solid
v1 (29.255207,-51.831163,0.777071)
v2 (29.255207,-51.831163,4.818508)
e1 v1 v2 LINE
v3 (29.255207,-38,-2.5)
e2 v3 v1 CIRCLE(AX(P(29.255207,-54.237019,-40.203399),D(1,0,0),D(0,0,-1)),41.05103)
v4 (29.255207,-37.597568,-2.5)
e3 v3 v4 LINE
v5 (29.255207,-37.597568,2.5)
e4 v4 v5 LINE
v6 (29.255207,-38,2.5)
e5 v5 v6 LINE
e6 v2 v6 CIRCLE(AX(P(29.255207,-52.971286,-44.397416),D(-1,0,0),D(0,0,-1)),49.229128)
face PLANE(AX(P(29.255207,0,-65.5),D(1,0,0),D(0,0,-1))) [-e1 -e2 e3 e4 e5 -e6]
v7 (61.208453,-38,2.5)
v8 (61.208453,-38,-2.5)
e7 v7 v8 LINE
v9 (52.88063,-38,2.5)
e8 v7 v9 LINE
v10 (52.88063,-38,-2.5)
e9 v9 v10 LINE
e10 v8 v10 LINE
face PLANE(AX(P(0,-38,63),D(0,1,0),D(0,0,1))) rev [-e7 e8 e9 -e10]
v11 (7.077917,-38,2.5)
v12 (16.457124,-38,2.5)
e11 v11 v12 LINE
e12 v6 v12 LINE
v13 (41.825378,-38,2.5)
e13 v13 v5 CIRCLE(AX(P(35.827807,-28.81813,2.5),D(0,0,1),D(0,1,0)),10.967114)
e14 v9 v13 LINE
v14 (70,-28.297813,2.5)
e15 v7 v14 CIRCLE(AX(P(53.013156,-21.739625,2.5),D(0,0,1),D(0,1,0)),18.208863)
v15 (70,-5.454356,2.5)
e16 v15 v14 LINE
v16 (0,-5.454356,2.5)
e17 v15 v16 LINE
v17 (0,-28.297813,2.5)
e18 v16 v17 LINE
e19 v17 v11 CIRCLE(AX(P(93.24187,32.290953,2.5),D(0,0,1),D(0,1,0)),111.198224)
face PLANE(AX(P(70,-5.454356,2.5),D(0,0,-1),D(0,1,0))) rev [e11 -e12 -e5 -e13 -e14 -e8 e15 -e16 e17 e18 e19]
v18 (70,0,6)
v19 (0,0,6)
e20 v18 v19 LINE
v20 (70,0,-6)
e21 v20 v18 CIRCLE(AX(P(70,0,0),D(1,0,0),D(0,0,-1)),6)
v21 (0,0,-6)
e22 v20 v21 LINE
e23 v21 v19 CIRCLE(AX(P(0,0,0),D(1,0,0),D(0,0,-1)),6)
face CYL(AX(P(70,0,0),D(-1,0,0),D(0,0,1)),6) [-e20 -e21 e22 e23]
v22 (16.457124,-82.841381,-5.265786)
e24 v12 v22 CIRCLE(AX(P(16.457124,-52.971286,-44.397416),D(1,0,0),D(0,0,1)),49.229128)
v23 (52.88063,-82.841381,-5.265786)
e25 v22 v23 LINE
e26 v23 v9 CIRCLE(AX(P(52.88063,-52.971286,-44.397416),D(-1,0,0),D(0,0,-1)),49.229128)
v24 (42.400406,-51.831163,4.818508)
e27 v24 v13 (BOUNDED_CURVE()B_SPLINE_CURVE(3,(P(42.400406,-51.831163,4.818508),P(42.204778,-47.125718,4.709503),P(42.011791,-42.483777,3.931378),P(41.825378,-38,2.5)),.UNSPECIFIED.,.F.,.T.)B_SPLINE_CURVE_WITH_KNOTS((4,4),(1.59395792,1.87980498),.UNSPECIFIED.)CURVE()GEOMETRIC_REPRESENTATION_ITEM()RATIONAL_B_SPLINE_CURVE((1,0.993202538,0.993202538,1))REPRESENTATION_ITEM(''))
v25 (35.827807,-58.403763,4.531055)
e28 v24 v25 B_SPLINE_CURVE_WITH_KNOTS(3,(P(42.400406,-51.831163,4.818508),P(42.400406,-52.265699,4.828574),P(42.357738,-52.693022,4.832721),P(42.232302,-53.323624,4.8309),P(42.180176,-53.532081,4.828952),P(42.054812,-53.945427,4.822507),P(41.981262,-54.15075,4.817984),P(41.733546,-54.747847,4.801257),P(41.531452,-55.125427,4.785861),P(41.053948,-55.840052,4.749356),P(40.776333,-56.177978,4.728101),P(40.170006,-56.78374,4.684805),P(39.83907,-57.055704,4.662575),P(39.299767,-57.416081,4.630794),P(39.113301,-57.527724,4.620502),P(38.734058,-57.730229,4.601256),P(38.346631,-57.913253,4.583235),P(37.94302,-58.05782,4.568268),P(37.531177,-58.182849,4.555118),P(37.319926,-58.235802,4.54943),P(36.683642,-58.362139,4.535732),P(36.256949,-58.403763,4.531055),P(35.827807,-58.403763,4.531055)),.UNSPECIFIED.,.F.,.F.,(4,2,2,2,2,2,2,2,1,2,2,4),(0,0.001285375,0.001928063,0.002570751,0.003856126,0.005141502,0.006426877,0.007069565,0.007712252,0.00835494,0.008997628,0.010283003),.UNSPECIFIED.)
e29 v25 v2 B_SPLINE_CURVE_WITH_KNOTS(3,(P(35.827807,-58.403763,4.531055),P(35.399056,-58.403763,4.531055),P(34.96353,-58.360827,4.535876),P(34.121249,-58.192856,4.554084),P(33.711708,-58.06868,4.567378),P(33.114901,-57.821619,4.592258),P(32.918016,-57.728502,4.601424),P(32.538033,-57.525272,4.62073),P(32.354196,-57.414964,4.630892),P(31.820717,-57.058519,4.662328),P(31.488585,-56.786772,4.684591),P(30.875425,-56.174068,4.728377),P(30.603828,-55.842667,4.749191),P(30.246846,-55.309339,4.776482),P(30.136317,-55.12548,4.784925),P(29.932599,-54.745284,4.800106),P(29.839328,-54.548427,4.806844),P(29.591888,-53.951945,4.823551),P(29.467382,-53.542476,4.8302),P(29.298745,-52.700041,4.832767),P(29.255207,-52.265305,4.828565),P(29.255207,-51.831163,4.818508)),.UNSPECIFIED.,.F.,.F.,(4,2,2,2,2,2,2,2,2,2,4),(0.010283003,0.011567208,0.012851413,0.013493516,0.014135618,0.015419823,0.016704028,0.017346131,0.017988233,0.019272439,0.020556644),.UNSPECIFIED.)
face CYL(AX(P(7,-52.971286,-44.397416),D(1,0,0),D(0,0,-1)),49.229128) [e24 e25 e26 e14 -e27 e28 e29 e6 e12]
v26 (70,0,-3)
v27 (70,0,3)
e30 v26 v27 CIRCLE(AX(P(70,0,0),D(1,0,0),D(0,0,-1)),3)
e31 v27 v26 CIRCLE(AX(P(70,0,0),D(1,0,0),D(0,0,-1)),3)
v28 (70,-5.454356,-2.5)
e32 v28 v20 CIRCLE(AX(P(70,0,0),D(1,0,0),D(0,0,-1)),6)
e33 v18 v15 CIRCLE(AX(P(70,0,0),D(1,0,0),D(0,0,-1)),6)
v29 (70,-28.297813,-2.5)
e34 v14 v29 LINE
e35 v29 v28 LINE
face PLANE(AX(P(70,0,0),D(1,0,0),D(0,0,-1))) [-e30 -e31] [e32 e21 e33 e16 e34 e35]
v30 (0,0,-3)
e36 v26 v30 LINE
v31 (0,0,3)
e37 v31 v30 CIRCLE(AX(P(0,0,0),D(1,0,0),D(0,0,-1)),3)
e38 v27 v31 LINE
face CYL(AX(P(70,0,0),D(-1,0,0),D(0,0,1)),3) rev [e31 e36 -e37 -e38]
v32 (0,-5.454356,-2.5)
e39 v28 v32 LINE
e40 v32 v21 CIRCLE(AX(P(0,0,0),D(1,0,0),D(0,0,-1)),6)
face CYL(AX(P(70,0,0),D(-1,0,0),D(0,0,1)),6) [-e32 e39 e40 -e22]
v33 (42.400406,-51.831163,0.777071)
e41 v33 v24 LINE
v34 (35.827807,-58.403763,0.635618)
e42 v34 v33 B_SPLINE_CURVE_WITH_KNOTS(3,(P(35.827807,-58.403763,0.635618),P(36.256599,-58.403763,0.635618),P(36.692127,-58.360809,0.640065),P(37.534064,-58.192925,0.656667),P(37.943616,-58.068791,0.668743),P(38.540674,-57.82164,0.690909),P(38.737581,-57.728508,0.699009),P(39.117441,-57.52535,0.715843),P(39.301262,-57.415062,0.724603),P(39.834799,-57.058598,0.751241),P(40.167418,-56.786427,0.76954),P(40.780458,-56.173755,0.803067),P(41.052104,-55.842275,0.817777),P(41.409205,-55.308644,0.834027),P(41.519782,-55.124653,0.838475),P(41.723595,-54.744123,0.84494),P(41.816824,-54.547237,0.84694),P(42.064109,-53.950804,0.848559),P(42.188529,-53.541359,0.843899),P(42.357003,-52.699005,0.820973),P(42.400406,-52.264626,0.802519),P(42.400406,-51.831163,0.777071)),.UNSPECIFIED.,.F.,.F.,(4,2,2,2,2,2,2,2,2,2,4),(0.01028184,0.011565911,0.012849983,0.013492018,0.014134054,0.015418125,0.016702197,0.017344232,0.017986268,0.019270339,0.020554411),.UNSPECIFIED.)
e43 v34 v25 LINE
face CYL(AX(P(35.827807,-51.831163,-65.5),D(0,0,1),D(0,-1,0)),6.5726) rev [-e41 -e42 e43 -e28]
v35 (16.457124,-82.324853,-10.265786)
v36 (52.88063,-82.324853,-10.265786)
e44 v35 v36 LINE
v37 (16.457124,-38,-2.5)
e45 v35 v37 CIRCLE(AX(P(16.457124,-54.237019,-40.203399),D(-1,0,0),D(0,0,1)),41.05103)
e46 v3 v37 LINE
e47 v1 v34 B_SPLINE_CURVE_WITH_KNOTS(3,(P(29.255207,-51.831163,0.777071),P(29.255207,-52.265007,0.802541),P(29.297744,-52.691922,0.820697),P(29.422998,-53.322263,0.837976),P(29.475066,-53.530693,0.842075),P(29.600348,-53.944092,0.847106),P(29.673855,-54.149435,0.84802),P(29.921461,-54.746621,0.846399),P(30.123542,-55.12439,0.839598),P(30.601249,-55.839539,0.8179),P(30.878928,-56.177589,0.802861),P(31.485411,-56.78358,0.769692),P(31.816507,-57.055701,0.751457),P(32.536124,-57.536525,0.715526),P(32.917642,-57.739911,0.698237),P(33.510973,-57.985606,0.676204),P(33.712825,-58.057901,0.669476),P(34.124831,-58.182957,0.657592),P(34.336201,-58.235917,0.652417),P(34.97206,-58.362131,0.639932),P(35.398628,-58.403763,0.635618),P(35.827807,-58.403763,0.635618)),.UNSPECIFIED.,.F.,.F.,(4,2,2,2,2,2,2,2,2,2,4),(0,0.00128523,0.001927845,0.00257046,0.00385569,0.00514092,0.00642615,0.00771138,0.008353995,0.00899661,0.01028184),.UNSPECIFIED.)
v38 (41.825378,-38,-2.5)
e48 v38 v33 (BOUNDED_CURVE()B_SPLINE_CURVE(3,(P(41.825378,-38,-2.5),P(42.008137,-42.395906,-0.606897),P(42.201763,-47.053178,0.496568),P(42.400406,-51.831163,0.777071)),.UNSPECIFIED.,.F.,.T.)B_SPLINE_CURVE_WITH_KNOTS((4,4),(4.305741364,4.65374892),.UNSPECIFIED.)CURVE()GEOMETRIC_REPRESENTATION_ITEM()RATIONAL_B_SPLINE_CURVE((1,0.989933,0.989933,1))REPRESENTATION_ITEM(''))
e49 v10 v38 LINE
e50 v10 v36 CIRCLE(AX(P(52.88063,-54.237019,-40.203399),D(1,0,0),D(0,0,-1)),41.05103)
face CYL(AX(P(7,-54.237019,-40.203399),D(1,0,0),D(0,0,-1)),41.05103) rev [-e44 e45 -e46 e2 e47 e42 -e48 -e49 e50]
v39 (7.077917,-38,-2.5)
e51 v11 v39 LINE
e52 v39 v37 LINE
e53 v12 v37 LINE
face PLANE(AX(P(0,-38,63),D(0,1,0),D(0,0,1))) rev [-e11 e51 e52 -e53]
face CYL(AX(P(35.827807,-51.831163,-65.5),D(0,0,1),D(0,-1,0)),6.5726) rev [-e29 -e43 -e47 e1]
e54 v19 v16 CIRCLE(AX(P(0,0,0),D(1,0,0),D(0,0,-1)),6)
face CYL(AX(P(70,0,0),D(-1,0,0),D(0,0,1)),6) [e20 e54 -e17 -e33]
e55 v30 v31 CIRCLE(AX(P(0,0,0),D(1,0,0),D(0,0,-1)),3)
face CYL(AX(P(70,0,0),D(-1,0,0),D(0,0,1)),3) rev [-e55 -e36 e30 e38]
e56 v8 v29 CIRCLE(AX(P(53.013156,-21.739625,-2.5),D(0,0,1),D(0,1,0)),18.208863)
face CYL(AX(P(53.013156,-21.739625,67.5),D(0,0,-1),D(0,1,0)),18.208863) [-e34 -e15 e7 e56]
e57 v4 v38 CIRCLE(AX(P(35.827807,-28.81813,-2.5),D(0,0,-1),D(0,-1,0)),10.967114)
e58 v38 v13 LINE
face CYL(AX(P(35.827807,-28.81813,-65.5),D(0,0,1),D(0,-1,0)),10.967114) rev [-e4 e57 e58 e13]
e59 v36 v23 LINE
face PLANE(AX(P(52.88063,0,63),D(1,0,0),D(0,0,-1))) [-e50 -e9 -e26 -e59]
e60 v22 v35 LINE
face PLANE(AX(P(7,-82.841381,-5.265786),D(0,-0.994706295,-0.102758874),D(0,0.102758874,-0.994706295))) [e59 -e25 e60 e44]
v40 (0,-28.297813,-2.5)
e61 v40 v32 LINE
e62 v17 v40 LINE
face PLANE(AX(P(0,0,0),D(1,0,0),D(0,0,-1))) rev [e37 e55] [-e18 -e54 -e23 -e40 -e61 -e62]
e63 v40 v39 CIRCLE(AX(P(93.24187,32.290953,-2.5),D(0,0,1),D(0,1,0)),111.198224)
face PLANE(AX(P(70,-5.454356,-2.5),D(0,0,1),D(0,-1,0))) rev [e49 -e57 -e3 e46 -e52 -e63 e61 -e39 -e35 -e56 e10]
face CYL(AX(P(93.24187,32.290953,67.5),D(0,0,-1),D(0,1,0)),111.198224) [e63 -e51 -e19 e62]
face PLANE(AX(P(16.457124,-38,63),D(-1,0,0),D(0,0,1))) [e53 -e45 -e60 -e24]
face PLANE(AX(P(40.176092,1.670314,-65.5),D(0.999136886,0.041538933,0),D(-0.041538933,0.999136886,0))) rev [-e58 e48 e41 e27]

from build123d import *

# Parameters (mm, degrees)
BARREL_AND_PLATE_PROFILE_SKETCH_R = 3
BARREL_AND_PLATE_70MM_DEPTH       = 70
PLATE_PROFILE_TRIM_DEPTH          = 70
LOWER_PLATE_DEPTH                 = 63
KEYHOLE_CUT_DEPTH                 = 63
KEYHOLE_CUT_DEPTH_BACK            = 63
KEYHOLE_SKETCH_W                  = 3.828036988
KEYHOLE_SKETCH_H                  = 46.115634491
KEYHOLE_SKETCH_W_2                = 17.383946001
CORNER_CHAMFER_CUT_DEPTH          = 63
CORNER_CHAMFER_CUT_DEPTH_BACK     = 63
CORNER_CHAMFER_SKETCH_W           = 7.615823962
CORNER_CHAMFER_SKETCH_H           = 47.440125615
CURVED_LOWER_EDGE_CUT_DEPTH       = 63
CURVED_LOWER_EDGE_CUT_DEPTH_BACK  = 63


with BuildPart() as part:
    # Barrel and Plate Profile Sketch → Barrel and Plate 70mm (new body)
    with BuildSketch(Plane(origin=(0, 0, 0), x_dir=(0, 0, -1), z_dir=(1, 0, 0))):
        with BuildLine():
            Line((-2.5, -5.454356057), (-2.5, -38))
            Line((-2.5, -38), (2.5, -38))
            Line((2.5, -38), (2.5, -5.454356057))
            ThreePointArc((2.5, -5.454356057), (0, 6), (-2.5, -5.454356057))
        make_face()
        Circle(BARREL_AND_PLATE_PROFILE_SKETCH_R, mode=Mode.SUBTRACT)
    extrude(amount=BARREL_AND_PLATE_70MM_DEPTH)

    # Plate Profile Trim Sketch → Plate Profile Trim (cut)
    with BuildSketch(Plane(origin=(0, 0, -2.5), x_dir=(-1, 0, 0), z_dir=(0, 0, -1))):
        with BuildLine():
            Line((-70, -28.297812678), (-70, -38))
            Line((-70, -38), (-61.208453248, -38))
            ThreePointArc((-61.208453248, -38), (-66.50641986, -33.966420344), (-70, -28.297812678))
        make_face()
        with BuildLine():
            Line((-7.077917117, -38), (0, -38))
            Line((0, -38), (0, -28.297812678))
            ThreePointArc((0, -28.297812678), (-3.407881829, -33.244529129), (-7.077917117, -38))
        make_face()
    extrude(amount=-PLATE_PROFILE_TRIM_DEPTH, mode=Mode.SUBTRACT)

    # Lower Plate Sketch → Lower Plate (add)
    with BuildSketch(Plane(origin=(70, 0, 0), x_dir=(0, 0, -1), z_dir=(1, 0, 0))):
        with BuildLine():
            Line((5.265785985, -82.841381432), (10.265785985, -82.324852713))
            ThreePointArc((10.265785985, -82.324852713), (-0.231731323, -61.32131925), (2.5, -38))
            Line((2.5, -38), (-2.5, -38))
            ThreePointArc((-2.5, -38), (-4.109661448, -61.371910347), (5.265785985, -82.841381432))
        make_face()
    extrude(amount=-LOWER_PLATE_DEPTH)

    # Keyhole Sketch → Keyhole Cut (cut, two sides: drawn at the far end of the back side and taken through both)
    with BuildSketch(Plane.XY.offset(-KEYHOLE_CUT_DEPTH_BACK)):
        with Locations((8.914018494, -61.057817246)):
            Rectangle(KEYHOLE_SKETCH_W, KEYHOLE_SKETCH_H)
        with Locations((61.572603173, -61.057817246)):
            Rectangle(KEYHOLE_SKETCH_W_2, KEYHOLE_SKETCH_H)
    extrude(amount=KEYHOLE_CUT_DEPTH + KEYHOLE_CUT_DEPTH_BACK, mode=Mode.SUBTRACT)

    # Corner Chamfer Sketch → Corner Chamfer Cut (cut, two sides: drawn at the far end of the back side and taken through both)
    with BuildSketch(Plane.XY.offset(-CORNER_CHAMFER_CUT_DEPTH_BACK)):
        with Locations((12.649212284, -61.720062807)):
            Rectangle(CORNER_CHAMFER_SKETCH_W, CORNER_CHAMFER_SKETCH_H)
    extrude(amount=CORNER_CHAMFER_CUT_DEPTH + CORNER_CHAMFER_CUT_DEPTH_BACK, mode=Mode.SUBTRACT)

    # Curved Lower Edge Sketch → Curved Lower Edge Cut (cut, two sides: drawn at the far end of the back side and taken through both)
    with BuildSketch(Plane(origin=(0, 0, -2.5), x_dir=(-1, 0, 0), z_dir=(0, 0, -1)).offset(-CURVED_LOWER_EDGE_CUT_DEPTH_BACK)):
        with BuildLine():
            Line((-42.377724671, -51.285597096), (-42.400406488, -51.831163346))
            ThreePointArc((-42.400406488, -51.831163346), (-35.827806952, -58.403762881), (-29.255207417, -51.831163346))
            Line((-29.255207417, -51.831163346), (-29.255207417, -38))
            Line((-29.255207417, -38), (-41.825378407, -38))
            Line((-41.825378407, -38), (-42.377724671, -51.285597096))
        make_face()
        with BuildLine():
            ThreePointArc((-29.255207417, -37.597568213), (-36.178737372, -17.856631692), (-41.825378407, -38))
            Line((-41.825378407, -38), (-29.255207417, -38))
            Line((-29.255207417, -38), (-29.255207417, -37.597568213))
        make_face()
    extrude(amount=CURVED_LOWER_EDGE_CUT_DEPTH + CURVED_LOWER_EDGE_CUT_DEPTH_BACK, mode=Mode.SUBTRACT)


solid = part.part
